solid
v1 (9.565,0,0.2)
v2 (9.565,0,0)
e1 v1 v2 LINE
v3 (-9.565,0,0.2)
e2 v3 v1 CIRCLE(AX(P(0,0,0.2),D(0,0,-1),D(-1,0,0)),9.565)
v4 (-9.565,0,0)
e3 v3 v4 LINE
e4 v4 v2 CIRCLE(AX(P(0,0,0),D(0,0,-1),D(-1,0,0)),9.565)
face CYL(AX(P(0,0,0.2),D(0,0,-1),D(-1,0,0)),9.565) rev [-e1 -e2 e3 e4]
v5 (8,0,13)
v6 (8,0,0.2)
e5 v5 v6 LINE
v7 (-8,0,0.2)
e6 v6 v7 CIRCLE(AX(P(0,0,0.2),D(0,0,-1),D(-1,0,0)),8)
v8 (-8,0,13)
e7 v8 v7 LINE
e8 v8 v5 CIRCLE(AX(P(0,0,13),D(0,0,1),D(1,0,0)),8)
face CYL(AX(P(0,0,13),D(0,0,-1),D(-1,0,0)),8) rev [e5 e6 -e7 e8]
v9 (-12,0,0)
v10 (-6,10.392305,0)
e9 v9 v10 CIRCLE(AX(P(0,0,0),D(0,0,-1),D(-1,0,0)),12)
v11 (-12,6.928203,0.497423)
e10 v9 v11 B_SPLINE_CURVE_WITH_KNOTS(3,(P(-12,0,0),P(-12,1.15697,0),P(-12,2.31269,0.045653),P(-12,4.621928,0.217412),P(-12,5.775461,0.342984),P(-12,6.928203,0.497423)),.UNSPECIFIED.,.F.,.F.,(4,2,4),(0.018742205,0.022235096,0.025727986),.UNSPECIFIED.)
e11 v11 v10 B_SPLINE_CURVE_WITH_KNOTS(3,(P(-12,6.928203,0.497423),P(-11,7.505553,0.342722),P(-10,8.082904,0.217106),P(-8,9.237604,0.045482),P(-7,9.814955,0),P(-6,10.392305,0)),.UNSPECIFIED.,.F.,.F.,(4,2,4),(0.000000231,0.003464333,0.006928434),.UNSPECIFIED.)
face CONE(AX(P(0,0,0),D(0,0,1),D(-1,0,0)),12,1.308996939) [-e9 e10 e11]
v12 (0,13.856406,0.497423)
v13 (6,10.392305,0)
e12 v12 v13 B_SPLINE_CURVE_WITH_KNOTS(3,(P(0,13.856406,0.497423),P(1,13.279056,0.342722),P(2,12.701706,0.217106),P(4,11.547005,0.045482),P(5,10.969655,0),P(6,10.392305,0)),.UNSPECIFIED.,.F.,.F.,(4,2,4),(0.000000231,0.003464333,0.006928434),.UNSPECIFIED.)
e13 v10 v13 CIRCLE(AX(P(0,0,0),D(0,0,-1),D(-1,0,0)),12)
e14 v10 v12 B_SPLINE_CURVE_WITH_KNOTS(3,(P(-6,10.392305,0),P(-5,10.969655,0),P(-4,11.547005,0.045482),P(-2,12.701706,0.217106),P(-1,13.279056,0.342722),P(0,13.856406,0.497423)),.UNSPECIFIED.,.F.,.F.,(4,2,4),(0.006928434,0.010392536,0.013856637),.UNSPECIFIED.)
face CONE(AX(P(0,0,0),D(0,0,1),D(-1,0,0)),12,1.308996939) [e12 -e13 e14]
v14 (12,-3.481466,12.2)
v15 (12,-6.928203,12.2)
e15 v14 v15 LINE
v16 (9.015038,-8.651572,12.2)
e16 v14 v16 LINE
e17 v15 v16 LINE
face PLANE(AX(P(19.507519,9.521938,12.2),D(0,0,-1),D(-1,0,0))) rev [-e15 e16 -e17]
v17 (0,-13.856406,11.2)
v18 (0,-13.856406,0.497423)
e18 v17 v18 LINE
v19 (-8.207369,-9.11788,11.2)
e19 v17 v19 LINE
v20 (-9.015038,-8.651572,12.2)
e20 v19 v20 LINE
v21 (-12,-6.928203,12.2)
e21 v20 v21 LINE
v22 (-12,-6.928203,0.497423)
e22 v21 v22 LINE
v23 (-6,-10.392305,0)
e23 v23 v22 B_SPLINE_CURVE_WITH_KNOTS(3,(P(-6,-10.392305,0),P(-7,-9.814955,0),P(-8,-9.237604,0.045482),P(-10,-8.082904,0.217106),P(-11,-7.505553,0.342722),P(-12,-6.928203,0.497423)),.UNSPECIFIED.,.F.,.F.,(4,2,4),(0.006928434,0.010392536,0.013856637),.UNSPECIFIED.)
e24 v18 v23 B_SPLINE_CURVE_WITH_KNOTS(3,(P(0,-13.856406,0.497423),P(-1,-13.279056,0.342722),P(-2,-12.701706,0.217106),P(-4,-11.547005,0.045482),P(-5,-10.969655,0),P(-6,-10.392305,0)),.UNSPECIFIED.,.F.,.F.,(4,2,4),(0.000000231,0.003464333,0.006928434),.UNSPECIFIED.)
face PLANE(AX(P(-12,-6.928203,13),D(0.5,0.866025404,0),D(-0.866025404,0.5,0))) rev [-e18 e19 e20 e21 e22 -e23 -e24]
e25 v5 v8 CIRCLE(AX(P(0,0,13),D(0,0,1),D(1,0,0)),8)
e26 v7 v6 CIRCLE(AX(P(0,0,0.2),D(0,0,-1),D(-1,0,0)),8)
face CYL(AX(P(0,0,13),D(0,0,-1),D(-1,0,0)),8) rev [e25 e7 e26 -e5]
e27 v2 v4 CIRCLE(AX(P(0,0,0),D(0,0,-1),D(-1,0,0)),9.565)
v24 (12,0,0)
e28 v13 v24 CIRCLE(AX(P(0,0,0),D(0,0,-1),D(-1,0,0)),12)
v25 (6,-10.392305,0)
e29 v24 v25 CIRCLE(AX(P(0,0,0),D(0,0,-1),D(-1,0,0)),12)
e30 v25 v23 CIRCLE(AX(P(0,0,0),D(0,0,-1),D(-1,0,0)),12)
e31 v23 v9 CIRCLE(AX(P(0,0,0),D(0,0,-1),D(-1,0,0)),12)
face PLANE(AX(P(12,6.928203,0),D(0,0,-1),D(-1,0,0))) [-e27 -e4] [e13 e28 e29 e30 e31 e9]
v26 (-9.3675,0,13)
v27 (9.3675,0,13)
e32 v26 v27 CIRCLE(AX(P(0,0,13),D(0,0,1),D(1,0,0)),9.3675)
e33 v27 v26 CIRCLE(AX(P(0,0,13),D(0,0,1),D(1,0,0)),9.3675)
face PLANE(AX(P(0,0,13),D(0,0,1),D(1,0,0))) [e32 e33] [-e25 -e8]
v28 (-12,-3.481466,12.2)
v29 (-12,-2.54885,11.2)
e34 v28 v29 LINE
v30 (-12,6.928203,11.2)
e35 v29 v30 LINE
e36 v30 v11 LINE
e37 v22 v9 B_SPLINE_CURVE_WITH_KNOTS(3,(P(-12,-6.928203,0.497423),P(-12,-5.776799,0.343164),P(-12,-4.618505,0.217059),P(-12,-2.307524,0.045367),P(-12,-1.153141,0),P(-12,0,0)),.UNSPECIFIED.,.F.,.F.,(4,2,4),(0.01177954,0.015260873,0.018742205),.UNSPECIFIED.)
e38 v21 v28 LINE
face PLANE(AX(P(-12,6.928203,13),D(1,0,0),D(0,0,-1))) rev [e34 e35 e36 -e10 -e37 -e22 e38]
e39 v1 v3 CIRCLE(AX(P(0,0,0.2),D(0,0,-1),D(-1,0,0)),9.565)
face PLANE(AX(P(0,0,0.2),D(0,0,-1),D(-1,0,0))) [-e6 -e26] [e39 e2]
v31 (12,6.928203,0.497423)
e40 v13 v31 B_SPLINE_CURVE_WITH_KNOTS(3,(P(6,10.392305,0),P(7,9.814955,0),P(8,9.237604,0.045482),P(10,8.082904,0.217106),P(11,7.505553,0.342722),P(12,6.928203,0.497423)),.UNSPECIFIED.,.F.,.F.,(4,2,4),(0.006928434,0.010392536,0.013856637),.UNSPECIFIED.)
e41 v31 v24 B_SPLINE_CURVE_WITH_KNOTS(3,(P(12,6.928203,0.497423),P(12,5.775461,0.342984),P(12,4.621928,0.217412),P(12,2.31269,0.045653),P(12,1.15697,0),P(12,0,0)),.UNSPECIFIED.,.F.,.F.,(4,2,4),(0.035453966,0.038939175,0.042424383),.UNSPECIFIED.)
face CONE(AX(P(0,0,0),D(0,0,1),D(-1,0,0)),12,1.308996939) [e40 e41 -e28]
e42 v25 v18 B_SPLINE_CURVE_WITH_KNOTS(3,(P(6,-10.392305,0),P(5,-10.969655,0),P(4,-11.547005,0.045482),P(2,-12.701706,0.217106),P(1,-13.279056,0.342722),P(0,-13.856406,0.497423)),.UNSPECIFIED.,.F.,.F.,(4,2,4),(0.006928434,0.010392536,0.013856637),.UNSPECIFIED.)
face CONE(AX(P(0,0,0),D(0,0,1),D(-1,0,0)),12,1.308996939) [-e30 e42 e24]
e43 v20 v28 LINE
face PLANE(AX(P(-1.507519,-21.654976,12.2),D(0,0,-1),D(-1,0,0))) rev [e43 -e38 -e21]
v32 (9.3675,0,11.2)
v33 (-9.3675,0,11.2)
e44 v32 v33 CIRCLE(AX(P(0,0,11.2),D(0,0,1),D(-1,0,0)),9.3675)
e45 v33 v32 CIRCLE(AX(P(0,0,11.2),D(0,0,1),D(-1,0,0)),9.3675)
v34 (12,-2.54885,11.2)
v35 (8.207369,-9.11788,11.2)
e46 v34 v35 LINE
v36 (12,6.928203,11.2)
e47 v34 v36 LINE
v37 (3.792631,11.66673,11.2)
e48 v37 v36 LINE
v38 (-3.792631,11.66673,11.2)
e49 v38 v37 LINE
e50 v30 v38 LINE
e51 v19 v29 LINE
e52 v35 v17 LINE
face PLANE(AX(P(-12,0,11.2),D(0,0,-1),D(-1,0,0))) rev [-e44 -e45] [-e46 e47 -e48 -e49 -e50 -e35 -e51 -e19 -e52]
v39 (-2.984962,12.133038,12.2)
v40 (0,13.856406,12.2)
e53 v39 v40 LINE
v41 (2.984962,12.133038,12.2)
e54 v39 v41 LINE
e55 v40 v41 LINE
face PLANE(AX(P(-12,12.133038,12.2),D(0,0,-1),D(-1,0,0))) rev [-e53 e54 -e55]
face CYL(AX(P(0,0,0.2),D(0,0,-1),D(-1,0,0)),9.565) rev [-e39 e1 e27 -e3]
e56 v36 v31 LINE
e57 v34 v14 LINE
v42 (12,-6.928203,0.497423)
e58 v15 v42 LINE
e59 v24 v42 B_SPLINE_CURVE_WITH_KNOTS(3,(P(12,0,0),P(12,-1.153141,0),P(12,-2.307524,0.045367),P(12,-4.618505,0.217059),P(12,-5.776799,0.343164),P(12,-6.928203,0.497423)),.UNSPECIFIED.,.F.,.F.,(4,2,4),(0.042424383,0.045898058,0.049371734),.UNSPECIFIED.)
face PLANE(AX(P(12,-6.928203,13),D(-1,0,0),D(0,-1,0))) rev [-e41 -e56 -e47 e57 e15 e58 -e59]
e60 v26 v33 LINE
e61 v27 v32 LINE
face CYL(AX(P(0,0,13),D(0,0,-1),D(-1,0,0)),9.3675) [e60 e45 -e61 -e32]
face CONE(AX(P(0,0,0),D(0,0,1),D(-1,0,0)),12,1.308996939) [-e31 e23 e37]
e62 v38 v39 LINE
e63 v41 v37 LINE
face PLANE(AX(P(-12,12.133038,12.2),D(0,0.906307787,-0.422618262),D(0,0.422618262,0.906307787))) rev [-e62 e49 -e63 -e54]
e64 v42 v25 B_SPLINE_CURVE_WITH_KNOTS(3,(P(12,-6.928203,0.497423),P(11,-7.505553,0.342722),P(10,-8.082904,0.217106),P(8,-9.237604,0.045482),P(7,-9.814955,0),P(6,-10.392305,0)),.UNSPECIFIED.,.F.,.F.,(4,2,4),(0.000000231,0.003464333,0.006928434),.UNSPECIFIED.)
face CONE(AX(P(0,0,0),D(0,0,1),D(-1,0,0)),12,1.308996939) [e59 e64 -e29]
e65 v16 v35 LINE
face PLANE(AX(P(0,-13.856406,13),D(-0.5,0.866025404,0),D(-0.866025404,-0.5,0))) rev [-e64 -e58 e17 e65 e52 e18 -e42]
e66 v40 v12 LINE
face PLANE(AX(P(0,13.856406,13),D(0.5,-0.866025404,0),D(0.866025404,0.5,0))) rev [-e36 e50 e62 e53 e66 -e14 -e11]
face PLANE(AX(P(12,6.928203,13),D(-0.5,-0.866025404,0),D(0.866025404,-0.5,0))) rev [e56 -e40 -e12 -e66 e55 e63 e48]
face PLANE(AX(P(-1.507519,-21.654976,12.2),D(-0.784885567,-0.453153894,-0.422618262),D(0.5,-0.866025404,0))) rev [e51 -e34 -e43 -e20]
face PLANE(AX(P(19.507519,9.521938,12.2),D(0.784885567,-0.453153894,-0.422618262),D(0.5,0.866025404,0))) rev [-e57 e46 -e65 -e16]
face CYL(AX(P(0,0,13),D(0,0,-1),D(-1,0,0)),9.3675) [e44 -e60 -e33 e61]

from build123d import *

# Parameters (mm, degrees)
SKETCH_1_R               = 8
EXTRUDE_1_DEPTH          = 13
CUT_EXTRUDE_2_DEPTH      = 23.472205054
PATTERN_CIRCULAR_1_COUNT = 3
SKETCH_2_R               = 9.3675
SKETCH_2_R_2             = 8
EXTRUDE_2_DEPTH          = 1.8
SKETCH_4_OUTSIDE_W       = 208.978
SKETCH_4_OUTSIDE_H       = 212.69
SKETCH_4_OUTSIDE_R       = 12
CUT_EXTRUDE_3_DEPTH      = 23.472205054
CUT_EXTRUDE_3_DRAFT      = -75
SKETCH_5_R               = 9.565
CUT_EXTRUDE_4_DEPTH      = 0.2


with BuildPart() as part:
    # 草图1 → 拉伸1 (new body)
    with BuildSketch(Plane.XY):
        Polygon((0, 13.856406461), (-12, 6.92820323), (-12, -6.92820323), (0, -13.856406461), (12, -6.92820323), (12, 6.92820323), align=None)
        with Locations(Location((0, 0, 0), (0, 0, 180))):
            Circle(SKETCH_1_R, mode=Mode.SUBTRACT)
    extrude(amount=EXTRUDE_1_DEPTH)

    # 草图3 → 切除-拉伸2 (cut, symmetric)
    with BuildSketch(Plane(origin=(0, 0, 0), x_dir=(0, 0, -1), z_dir=(1, 0, 0))):
        Polygon((-12.2, 12.133037667), (-11.2, 11.666730008), (-11.2, 0), (-13, 0), (-13, 13.856406461), (-12.2, 13.856406461), align=None)
    cut_extrude_2 = extrude(amount=CUT_EXTRUDE_2_DEPTH, both=True, mode=Mode.SUBTRACT)

    # 阵列(圆周)1: 切除-拉伸2 ×3 about axis
    pattern_circular_1_axis = Axis((0, 0, 0), (0, 0, 1))
    for i in range(1, PATTERN_CIRCULAR_1_COUNT):
        add(cut_extrude_2.rotate(pattern_circular_1_axis, i * 360 / PATTERN_CIRCULAR_1_COUNT), mode=Mode.SUBTRACT)

    # 草图2 → 拉伸2 (add)
    with BuildSketch(Plane.XY.offset(11.2)):
        with Locations(Location((0, 0, 0), (0, 0, 180))):
            Circle(SKETCH_2_R)
        with Locations(Location((0, 0, 0), (0, 0, 180))):
            Circle(SKETCH_2_R_2, mode=Mode.SUBTRACT)
    extrude(amount=EXTRUDE_2_DEPTH)


with BuildPart() as cut_extrude_3_tool:
    # 草图4 outside → 切除-拉伸3 (with draft: the straight prism first)
    with BuildSketch(Plane(origin=(0, 0, 0), x_dir=(-1, 0, 0), z_dir=(0, 0, -1))):
        Rectangle(SKETCH_4_OUTSIDE_W, SKETCH_4_OUTSIDE_H)
        Circle(SKETCH_4_OUTSIDE_R, mode=Mode.SUBTRACT)
    extrude(amount=-CUT_EXTRUDE_3_DEPTH)
    # 切除-拉伸3: the draft: its side faces are tilted about the plane it starts from
    cut_extrude_3_sides = [cut_extrude_3_tool.faces().sort_by_distance(p)[0] for p in [
        (0, -106.345, 11.736102527),
        (-104.489, 0, 11.736102527),
        (0, 106.345, 11.736102527),
        (104.489, 0, 11.736102527),
        (12, 0, 11.736102527),
    ]]
    draft(cut_extrude_3_sides, Plane(origin=(0, 0, 0), x_dir=(-1, 0, 0), z_dir=(0, 0, -1)), CUT_EXTRUDE_3_DRAFT)


with BuildPart() as part_1:
    add(part.part)

    # 切除-拉伸3: cut by cut_extrude_3_tool
    add(cut_extrude_3_tool.part, mode=Mode.SUBTRACT)

    # 草图5 → 切除-拉伸4 (cut)
    with BuildSketch(Plane(origin=(0, 0, 0), x_dir=(-1, 0, 0), z_dir=(0, 0, -1))):
        Circle(SKETCH_5_R)
    extrude(amount=-CUT_EXTRUDE_4_DEPTH, mode=Mode.SUBTRACT)


solid = part_1.part
